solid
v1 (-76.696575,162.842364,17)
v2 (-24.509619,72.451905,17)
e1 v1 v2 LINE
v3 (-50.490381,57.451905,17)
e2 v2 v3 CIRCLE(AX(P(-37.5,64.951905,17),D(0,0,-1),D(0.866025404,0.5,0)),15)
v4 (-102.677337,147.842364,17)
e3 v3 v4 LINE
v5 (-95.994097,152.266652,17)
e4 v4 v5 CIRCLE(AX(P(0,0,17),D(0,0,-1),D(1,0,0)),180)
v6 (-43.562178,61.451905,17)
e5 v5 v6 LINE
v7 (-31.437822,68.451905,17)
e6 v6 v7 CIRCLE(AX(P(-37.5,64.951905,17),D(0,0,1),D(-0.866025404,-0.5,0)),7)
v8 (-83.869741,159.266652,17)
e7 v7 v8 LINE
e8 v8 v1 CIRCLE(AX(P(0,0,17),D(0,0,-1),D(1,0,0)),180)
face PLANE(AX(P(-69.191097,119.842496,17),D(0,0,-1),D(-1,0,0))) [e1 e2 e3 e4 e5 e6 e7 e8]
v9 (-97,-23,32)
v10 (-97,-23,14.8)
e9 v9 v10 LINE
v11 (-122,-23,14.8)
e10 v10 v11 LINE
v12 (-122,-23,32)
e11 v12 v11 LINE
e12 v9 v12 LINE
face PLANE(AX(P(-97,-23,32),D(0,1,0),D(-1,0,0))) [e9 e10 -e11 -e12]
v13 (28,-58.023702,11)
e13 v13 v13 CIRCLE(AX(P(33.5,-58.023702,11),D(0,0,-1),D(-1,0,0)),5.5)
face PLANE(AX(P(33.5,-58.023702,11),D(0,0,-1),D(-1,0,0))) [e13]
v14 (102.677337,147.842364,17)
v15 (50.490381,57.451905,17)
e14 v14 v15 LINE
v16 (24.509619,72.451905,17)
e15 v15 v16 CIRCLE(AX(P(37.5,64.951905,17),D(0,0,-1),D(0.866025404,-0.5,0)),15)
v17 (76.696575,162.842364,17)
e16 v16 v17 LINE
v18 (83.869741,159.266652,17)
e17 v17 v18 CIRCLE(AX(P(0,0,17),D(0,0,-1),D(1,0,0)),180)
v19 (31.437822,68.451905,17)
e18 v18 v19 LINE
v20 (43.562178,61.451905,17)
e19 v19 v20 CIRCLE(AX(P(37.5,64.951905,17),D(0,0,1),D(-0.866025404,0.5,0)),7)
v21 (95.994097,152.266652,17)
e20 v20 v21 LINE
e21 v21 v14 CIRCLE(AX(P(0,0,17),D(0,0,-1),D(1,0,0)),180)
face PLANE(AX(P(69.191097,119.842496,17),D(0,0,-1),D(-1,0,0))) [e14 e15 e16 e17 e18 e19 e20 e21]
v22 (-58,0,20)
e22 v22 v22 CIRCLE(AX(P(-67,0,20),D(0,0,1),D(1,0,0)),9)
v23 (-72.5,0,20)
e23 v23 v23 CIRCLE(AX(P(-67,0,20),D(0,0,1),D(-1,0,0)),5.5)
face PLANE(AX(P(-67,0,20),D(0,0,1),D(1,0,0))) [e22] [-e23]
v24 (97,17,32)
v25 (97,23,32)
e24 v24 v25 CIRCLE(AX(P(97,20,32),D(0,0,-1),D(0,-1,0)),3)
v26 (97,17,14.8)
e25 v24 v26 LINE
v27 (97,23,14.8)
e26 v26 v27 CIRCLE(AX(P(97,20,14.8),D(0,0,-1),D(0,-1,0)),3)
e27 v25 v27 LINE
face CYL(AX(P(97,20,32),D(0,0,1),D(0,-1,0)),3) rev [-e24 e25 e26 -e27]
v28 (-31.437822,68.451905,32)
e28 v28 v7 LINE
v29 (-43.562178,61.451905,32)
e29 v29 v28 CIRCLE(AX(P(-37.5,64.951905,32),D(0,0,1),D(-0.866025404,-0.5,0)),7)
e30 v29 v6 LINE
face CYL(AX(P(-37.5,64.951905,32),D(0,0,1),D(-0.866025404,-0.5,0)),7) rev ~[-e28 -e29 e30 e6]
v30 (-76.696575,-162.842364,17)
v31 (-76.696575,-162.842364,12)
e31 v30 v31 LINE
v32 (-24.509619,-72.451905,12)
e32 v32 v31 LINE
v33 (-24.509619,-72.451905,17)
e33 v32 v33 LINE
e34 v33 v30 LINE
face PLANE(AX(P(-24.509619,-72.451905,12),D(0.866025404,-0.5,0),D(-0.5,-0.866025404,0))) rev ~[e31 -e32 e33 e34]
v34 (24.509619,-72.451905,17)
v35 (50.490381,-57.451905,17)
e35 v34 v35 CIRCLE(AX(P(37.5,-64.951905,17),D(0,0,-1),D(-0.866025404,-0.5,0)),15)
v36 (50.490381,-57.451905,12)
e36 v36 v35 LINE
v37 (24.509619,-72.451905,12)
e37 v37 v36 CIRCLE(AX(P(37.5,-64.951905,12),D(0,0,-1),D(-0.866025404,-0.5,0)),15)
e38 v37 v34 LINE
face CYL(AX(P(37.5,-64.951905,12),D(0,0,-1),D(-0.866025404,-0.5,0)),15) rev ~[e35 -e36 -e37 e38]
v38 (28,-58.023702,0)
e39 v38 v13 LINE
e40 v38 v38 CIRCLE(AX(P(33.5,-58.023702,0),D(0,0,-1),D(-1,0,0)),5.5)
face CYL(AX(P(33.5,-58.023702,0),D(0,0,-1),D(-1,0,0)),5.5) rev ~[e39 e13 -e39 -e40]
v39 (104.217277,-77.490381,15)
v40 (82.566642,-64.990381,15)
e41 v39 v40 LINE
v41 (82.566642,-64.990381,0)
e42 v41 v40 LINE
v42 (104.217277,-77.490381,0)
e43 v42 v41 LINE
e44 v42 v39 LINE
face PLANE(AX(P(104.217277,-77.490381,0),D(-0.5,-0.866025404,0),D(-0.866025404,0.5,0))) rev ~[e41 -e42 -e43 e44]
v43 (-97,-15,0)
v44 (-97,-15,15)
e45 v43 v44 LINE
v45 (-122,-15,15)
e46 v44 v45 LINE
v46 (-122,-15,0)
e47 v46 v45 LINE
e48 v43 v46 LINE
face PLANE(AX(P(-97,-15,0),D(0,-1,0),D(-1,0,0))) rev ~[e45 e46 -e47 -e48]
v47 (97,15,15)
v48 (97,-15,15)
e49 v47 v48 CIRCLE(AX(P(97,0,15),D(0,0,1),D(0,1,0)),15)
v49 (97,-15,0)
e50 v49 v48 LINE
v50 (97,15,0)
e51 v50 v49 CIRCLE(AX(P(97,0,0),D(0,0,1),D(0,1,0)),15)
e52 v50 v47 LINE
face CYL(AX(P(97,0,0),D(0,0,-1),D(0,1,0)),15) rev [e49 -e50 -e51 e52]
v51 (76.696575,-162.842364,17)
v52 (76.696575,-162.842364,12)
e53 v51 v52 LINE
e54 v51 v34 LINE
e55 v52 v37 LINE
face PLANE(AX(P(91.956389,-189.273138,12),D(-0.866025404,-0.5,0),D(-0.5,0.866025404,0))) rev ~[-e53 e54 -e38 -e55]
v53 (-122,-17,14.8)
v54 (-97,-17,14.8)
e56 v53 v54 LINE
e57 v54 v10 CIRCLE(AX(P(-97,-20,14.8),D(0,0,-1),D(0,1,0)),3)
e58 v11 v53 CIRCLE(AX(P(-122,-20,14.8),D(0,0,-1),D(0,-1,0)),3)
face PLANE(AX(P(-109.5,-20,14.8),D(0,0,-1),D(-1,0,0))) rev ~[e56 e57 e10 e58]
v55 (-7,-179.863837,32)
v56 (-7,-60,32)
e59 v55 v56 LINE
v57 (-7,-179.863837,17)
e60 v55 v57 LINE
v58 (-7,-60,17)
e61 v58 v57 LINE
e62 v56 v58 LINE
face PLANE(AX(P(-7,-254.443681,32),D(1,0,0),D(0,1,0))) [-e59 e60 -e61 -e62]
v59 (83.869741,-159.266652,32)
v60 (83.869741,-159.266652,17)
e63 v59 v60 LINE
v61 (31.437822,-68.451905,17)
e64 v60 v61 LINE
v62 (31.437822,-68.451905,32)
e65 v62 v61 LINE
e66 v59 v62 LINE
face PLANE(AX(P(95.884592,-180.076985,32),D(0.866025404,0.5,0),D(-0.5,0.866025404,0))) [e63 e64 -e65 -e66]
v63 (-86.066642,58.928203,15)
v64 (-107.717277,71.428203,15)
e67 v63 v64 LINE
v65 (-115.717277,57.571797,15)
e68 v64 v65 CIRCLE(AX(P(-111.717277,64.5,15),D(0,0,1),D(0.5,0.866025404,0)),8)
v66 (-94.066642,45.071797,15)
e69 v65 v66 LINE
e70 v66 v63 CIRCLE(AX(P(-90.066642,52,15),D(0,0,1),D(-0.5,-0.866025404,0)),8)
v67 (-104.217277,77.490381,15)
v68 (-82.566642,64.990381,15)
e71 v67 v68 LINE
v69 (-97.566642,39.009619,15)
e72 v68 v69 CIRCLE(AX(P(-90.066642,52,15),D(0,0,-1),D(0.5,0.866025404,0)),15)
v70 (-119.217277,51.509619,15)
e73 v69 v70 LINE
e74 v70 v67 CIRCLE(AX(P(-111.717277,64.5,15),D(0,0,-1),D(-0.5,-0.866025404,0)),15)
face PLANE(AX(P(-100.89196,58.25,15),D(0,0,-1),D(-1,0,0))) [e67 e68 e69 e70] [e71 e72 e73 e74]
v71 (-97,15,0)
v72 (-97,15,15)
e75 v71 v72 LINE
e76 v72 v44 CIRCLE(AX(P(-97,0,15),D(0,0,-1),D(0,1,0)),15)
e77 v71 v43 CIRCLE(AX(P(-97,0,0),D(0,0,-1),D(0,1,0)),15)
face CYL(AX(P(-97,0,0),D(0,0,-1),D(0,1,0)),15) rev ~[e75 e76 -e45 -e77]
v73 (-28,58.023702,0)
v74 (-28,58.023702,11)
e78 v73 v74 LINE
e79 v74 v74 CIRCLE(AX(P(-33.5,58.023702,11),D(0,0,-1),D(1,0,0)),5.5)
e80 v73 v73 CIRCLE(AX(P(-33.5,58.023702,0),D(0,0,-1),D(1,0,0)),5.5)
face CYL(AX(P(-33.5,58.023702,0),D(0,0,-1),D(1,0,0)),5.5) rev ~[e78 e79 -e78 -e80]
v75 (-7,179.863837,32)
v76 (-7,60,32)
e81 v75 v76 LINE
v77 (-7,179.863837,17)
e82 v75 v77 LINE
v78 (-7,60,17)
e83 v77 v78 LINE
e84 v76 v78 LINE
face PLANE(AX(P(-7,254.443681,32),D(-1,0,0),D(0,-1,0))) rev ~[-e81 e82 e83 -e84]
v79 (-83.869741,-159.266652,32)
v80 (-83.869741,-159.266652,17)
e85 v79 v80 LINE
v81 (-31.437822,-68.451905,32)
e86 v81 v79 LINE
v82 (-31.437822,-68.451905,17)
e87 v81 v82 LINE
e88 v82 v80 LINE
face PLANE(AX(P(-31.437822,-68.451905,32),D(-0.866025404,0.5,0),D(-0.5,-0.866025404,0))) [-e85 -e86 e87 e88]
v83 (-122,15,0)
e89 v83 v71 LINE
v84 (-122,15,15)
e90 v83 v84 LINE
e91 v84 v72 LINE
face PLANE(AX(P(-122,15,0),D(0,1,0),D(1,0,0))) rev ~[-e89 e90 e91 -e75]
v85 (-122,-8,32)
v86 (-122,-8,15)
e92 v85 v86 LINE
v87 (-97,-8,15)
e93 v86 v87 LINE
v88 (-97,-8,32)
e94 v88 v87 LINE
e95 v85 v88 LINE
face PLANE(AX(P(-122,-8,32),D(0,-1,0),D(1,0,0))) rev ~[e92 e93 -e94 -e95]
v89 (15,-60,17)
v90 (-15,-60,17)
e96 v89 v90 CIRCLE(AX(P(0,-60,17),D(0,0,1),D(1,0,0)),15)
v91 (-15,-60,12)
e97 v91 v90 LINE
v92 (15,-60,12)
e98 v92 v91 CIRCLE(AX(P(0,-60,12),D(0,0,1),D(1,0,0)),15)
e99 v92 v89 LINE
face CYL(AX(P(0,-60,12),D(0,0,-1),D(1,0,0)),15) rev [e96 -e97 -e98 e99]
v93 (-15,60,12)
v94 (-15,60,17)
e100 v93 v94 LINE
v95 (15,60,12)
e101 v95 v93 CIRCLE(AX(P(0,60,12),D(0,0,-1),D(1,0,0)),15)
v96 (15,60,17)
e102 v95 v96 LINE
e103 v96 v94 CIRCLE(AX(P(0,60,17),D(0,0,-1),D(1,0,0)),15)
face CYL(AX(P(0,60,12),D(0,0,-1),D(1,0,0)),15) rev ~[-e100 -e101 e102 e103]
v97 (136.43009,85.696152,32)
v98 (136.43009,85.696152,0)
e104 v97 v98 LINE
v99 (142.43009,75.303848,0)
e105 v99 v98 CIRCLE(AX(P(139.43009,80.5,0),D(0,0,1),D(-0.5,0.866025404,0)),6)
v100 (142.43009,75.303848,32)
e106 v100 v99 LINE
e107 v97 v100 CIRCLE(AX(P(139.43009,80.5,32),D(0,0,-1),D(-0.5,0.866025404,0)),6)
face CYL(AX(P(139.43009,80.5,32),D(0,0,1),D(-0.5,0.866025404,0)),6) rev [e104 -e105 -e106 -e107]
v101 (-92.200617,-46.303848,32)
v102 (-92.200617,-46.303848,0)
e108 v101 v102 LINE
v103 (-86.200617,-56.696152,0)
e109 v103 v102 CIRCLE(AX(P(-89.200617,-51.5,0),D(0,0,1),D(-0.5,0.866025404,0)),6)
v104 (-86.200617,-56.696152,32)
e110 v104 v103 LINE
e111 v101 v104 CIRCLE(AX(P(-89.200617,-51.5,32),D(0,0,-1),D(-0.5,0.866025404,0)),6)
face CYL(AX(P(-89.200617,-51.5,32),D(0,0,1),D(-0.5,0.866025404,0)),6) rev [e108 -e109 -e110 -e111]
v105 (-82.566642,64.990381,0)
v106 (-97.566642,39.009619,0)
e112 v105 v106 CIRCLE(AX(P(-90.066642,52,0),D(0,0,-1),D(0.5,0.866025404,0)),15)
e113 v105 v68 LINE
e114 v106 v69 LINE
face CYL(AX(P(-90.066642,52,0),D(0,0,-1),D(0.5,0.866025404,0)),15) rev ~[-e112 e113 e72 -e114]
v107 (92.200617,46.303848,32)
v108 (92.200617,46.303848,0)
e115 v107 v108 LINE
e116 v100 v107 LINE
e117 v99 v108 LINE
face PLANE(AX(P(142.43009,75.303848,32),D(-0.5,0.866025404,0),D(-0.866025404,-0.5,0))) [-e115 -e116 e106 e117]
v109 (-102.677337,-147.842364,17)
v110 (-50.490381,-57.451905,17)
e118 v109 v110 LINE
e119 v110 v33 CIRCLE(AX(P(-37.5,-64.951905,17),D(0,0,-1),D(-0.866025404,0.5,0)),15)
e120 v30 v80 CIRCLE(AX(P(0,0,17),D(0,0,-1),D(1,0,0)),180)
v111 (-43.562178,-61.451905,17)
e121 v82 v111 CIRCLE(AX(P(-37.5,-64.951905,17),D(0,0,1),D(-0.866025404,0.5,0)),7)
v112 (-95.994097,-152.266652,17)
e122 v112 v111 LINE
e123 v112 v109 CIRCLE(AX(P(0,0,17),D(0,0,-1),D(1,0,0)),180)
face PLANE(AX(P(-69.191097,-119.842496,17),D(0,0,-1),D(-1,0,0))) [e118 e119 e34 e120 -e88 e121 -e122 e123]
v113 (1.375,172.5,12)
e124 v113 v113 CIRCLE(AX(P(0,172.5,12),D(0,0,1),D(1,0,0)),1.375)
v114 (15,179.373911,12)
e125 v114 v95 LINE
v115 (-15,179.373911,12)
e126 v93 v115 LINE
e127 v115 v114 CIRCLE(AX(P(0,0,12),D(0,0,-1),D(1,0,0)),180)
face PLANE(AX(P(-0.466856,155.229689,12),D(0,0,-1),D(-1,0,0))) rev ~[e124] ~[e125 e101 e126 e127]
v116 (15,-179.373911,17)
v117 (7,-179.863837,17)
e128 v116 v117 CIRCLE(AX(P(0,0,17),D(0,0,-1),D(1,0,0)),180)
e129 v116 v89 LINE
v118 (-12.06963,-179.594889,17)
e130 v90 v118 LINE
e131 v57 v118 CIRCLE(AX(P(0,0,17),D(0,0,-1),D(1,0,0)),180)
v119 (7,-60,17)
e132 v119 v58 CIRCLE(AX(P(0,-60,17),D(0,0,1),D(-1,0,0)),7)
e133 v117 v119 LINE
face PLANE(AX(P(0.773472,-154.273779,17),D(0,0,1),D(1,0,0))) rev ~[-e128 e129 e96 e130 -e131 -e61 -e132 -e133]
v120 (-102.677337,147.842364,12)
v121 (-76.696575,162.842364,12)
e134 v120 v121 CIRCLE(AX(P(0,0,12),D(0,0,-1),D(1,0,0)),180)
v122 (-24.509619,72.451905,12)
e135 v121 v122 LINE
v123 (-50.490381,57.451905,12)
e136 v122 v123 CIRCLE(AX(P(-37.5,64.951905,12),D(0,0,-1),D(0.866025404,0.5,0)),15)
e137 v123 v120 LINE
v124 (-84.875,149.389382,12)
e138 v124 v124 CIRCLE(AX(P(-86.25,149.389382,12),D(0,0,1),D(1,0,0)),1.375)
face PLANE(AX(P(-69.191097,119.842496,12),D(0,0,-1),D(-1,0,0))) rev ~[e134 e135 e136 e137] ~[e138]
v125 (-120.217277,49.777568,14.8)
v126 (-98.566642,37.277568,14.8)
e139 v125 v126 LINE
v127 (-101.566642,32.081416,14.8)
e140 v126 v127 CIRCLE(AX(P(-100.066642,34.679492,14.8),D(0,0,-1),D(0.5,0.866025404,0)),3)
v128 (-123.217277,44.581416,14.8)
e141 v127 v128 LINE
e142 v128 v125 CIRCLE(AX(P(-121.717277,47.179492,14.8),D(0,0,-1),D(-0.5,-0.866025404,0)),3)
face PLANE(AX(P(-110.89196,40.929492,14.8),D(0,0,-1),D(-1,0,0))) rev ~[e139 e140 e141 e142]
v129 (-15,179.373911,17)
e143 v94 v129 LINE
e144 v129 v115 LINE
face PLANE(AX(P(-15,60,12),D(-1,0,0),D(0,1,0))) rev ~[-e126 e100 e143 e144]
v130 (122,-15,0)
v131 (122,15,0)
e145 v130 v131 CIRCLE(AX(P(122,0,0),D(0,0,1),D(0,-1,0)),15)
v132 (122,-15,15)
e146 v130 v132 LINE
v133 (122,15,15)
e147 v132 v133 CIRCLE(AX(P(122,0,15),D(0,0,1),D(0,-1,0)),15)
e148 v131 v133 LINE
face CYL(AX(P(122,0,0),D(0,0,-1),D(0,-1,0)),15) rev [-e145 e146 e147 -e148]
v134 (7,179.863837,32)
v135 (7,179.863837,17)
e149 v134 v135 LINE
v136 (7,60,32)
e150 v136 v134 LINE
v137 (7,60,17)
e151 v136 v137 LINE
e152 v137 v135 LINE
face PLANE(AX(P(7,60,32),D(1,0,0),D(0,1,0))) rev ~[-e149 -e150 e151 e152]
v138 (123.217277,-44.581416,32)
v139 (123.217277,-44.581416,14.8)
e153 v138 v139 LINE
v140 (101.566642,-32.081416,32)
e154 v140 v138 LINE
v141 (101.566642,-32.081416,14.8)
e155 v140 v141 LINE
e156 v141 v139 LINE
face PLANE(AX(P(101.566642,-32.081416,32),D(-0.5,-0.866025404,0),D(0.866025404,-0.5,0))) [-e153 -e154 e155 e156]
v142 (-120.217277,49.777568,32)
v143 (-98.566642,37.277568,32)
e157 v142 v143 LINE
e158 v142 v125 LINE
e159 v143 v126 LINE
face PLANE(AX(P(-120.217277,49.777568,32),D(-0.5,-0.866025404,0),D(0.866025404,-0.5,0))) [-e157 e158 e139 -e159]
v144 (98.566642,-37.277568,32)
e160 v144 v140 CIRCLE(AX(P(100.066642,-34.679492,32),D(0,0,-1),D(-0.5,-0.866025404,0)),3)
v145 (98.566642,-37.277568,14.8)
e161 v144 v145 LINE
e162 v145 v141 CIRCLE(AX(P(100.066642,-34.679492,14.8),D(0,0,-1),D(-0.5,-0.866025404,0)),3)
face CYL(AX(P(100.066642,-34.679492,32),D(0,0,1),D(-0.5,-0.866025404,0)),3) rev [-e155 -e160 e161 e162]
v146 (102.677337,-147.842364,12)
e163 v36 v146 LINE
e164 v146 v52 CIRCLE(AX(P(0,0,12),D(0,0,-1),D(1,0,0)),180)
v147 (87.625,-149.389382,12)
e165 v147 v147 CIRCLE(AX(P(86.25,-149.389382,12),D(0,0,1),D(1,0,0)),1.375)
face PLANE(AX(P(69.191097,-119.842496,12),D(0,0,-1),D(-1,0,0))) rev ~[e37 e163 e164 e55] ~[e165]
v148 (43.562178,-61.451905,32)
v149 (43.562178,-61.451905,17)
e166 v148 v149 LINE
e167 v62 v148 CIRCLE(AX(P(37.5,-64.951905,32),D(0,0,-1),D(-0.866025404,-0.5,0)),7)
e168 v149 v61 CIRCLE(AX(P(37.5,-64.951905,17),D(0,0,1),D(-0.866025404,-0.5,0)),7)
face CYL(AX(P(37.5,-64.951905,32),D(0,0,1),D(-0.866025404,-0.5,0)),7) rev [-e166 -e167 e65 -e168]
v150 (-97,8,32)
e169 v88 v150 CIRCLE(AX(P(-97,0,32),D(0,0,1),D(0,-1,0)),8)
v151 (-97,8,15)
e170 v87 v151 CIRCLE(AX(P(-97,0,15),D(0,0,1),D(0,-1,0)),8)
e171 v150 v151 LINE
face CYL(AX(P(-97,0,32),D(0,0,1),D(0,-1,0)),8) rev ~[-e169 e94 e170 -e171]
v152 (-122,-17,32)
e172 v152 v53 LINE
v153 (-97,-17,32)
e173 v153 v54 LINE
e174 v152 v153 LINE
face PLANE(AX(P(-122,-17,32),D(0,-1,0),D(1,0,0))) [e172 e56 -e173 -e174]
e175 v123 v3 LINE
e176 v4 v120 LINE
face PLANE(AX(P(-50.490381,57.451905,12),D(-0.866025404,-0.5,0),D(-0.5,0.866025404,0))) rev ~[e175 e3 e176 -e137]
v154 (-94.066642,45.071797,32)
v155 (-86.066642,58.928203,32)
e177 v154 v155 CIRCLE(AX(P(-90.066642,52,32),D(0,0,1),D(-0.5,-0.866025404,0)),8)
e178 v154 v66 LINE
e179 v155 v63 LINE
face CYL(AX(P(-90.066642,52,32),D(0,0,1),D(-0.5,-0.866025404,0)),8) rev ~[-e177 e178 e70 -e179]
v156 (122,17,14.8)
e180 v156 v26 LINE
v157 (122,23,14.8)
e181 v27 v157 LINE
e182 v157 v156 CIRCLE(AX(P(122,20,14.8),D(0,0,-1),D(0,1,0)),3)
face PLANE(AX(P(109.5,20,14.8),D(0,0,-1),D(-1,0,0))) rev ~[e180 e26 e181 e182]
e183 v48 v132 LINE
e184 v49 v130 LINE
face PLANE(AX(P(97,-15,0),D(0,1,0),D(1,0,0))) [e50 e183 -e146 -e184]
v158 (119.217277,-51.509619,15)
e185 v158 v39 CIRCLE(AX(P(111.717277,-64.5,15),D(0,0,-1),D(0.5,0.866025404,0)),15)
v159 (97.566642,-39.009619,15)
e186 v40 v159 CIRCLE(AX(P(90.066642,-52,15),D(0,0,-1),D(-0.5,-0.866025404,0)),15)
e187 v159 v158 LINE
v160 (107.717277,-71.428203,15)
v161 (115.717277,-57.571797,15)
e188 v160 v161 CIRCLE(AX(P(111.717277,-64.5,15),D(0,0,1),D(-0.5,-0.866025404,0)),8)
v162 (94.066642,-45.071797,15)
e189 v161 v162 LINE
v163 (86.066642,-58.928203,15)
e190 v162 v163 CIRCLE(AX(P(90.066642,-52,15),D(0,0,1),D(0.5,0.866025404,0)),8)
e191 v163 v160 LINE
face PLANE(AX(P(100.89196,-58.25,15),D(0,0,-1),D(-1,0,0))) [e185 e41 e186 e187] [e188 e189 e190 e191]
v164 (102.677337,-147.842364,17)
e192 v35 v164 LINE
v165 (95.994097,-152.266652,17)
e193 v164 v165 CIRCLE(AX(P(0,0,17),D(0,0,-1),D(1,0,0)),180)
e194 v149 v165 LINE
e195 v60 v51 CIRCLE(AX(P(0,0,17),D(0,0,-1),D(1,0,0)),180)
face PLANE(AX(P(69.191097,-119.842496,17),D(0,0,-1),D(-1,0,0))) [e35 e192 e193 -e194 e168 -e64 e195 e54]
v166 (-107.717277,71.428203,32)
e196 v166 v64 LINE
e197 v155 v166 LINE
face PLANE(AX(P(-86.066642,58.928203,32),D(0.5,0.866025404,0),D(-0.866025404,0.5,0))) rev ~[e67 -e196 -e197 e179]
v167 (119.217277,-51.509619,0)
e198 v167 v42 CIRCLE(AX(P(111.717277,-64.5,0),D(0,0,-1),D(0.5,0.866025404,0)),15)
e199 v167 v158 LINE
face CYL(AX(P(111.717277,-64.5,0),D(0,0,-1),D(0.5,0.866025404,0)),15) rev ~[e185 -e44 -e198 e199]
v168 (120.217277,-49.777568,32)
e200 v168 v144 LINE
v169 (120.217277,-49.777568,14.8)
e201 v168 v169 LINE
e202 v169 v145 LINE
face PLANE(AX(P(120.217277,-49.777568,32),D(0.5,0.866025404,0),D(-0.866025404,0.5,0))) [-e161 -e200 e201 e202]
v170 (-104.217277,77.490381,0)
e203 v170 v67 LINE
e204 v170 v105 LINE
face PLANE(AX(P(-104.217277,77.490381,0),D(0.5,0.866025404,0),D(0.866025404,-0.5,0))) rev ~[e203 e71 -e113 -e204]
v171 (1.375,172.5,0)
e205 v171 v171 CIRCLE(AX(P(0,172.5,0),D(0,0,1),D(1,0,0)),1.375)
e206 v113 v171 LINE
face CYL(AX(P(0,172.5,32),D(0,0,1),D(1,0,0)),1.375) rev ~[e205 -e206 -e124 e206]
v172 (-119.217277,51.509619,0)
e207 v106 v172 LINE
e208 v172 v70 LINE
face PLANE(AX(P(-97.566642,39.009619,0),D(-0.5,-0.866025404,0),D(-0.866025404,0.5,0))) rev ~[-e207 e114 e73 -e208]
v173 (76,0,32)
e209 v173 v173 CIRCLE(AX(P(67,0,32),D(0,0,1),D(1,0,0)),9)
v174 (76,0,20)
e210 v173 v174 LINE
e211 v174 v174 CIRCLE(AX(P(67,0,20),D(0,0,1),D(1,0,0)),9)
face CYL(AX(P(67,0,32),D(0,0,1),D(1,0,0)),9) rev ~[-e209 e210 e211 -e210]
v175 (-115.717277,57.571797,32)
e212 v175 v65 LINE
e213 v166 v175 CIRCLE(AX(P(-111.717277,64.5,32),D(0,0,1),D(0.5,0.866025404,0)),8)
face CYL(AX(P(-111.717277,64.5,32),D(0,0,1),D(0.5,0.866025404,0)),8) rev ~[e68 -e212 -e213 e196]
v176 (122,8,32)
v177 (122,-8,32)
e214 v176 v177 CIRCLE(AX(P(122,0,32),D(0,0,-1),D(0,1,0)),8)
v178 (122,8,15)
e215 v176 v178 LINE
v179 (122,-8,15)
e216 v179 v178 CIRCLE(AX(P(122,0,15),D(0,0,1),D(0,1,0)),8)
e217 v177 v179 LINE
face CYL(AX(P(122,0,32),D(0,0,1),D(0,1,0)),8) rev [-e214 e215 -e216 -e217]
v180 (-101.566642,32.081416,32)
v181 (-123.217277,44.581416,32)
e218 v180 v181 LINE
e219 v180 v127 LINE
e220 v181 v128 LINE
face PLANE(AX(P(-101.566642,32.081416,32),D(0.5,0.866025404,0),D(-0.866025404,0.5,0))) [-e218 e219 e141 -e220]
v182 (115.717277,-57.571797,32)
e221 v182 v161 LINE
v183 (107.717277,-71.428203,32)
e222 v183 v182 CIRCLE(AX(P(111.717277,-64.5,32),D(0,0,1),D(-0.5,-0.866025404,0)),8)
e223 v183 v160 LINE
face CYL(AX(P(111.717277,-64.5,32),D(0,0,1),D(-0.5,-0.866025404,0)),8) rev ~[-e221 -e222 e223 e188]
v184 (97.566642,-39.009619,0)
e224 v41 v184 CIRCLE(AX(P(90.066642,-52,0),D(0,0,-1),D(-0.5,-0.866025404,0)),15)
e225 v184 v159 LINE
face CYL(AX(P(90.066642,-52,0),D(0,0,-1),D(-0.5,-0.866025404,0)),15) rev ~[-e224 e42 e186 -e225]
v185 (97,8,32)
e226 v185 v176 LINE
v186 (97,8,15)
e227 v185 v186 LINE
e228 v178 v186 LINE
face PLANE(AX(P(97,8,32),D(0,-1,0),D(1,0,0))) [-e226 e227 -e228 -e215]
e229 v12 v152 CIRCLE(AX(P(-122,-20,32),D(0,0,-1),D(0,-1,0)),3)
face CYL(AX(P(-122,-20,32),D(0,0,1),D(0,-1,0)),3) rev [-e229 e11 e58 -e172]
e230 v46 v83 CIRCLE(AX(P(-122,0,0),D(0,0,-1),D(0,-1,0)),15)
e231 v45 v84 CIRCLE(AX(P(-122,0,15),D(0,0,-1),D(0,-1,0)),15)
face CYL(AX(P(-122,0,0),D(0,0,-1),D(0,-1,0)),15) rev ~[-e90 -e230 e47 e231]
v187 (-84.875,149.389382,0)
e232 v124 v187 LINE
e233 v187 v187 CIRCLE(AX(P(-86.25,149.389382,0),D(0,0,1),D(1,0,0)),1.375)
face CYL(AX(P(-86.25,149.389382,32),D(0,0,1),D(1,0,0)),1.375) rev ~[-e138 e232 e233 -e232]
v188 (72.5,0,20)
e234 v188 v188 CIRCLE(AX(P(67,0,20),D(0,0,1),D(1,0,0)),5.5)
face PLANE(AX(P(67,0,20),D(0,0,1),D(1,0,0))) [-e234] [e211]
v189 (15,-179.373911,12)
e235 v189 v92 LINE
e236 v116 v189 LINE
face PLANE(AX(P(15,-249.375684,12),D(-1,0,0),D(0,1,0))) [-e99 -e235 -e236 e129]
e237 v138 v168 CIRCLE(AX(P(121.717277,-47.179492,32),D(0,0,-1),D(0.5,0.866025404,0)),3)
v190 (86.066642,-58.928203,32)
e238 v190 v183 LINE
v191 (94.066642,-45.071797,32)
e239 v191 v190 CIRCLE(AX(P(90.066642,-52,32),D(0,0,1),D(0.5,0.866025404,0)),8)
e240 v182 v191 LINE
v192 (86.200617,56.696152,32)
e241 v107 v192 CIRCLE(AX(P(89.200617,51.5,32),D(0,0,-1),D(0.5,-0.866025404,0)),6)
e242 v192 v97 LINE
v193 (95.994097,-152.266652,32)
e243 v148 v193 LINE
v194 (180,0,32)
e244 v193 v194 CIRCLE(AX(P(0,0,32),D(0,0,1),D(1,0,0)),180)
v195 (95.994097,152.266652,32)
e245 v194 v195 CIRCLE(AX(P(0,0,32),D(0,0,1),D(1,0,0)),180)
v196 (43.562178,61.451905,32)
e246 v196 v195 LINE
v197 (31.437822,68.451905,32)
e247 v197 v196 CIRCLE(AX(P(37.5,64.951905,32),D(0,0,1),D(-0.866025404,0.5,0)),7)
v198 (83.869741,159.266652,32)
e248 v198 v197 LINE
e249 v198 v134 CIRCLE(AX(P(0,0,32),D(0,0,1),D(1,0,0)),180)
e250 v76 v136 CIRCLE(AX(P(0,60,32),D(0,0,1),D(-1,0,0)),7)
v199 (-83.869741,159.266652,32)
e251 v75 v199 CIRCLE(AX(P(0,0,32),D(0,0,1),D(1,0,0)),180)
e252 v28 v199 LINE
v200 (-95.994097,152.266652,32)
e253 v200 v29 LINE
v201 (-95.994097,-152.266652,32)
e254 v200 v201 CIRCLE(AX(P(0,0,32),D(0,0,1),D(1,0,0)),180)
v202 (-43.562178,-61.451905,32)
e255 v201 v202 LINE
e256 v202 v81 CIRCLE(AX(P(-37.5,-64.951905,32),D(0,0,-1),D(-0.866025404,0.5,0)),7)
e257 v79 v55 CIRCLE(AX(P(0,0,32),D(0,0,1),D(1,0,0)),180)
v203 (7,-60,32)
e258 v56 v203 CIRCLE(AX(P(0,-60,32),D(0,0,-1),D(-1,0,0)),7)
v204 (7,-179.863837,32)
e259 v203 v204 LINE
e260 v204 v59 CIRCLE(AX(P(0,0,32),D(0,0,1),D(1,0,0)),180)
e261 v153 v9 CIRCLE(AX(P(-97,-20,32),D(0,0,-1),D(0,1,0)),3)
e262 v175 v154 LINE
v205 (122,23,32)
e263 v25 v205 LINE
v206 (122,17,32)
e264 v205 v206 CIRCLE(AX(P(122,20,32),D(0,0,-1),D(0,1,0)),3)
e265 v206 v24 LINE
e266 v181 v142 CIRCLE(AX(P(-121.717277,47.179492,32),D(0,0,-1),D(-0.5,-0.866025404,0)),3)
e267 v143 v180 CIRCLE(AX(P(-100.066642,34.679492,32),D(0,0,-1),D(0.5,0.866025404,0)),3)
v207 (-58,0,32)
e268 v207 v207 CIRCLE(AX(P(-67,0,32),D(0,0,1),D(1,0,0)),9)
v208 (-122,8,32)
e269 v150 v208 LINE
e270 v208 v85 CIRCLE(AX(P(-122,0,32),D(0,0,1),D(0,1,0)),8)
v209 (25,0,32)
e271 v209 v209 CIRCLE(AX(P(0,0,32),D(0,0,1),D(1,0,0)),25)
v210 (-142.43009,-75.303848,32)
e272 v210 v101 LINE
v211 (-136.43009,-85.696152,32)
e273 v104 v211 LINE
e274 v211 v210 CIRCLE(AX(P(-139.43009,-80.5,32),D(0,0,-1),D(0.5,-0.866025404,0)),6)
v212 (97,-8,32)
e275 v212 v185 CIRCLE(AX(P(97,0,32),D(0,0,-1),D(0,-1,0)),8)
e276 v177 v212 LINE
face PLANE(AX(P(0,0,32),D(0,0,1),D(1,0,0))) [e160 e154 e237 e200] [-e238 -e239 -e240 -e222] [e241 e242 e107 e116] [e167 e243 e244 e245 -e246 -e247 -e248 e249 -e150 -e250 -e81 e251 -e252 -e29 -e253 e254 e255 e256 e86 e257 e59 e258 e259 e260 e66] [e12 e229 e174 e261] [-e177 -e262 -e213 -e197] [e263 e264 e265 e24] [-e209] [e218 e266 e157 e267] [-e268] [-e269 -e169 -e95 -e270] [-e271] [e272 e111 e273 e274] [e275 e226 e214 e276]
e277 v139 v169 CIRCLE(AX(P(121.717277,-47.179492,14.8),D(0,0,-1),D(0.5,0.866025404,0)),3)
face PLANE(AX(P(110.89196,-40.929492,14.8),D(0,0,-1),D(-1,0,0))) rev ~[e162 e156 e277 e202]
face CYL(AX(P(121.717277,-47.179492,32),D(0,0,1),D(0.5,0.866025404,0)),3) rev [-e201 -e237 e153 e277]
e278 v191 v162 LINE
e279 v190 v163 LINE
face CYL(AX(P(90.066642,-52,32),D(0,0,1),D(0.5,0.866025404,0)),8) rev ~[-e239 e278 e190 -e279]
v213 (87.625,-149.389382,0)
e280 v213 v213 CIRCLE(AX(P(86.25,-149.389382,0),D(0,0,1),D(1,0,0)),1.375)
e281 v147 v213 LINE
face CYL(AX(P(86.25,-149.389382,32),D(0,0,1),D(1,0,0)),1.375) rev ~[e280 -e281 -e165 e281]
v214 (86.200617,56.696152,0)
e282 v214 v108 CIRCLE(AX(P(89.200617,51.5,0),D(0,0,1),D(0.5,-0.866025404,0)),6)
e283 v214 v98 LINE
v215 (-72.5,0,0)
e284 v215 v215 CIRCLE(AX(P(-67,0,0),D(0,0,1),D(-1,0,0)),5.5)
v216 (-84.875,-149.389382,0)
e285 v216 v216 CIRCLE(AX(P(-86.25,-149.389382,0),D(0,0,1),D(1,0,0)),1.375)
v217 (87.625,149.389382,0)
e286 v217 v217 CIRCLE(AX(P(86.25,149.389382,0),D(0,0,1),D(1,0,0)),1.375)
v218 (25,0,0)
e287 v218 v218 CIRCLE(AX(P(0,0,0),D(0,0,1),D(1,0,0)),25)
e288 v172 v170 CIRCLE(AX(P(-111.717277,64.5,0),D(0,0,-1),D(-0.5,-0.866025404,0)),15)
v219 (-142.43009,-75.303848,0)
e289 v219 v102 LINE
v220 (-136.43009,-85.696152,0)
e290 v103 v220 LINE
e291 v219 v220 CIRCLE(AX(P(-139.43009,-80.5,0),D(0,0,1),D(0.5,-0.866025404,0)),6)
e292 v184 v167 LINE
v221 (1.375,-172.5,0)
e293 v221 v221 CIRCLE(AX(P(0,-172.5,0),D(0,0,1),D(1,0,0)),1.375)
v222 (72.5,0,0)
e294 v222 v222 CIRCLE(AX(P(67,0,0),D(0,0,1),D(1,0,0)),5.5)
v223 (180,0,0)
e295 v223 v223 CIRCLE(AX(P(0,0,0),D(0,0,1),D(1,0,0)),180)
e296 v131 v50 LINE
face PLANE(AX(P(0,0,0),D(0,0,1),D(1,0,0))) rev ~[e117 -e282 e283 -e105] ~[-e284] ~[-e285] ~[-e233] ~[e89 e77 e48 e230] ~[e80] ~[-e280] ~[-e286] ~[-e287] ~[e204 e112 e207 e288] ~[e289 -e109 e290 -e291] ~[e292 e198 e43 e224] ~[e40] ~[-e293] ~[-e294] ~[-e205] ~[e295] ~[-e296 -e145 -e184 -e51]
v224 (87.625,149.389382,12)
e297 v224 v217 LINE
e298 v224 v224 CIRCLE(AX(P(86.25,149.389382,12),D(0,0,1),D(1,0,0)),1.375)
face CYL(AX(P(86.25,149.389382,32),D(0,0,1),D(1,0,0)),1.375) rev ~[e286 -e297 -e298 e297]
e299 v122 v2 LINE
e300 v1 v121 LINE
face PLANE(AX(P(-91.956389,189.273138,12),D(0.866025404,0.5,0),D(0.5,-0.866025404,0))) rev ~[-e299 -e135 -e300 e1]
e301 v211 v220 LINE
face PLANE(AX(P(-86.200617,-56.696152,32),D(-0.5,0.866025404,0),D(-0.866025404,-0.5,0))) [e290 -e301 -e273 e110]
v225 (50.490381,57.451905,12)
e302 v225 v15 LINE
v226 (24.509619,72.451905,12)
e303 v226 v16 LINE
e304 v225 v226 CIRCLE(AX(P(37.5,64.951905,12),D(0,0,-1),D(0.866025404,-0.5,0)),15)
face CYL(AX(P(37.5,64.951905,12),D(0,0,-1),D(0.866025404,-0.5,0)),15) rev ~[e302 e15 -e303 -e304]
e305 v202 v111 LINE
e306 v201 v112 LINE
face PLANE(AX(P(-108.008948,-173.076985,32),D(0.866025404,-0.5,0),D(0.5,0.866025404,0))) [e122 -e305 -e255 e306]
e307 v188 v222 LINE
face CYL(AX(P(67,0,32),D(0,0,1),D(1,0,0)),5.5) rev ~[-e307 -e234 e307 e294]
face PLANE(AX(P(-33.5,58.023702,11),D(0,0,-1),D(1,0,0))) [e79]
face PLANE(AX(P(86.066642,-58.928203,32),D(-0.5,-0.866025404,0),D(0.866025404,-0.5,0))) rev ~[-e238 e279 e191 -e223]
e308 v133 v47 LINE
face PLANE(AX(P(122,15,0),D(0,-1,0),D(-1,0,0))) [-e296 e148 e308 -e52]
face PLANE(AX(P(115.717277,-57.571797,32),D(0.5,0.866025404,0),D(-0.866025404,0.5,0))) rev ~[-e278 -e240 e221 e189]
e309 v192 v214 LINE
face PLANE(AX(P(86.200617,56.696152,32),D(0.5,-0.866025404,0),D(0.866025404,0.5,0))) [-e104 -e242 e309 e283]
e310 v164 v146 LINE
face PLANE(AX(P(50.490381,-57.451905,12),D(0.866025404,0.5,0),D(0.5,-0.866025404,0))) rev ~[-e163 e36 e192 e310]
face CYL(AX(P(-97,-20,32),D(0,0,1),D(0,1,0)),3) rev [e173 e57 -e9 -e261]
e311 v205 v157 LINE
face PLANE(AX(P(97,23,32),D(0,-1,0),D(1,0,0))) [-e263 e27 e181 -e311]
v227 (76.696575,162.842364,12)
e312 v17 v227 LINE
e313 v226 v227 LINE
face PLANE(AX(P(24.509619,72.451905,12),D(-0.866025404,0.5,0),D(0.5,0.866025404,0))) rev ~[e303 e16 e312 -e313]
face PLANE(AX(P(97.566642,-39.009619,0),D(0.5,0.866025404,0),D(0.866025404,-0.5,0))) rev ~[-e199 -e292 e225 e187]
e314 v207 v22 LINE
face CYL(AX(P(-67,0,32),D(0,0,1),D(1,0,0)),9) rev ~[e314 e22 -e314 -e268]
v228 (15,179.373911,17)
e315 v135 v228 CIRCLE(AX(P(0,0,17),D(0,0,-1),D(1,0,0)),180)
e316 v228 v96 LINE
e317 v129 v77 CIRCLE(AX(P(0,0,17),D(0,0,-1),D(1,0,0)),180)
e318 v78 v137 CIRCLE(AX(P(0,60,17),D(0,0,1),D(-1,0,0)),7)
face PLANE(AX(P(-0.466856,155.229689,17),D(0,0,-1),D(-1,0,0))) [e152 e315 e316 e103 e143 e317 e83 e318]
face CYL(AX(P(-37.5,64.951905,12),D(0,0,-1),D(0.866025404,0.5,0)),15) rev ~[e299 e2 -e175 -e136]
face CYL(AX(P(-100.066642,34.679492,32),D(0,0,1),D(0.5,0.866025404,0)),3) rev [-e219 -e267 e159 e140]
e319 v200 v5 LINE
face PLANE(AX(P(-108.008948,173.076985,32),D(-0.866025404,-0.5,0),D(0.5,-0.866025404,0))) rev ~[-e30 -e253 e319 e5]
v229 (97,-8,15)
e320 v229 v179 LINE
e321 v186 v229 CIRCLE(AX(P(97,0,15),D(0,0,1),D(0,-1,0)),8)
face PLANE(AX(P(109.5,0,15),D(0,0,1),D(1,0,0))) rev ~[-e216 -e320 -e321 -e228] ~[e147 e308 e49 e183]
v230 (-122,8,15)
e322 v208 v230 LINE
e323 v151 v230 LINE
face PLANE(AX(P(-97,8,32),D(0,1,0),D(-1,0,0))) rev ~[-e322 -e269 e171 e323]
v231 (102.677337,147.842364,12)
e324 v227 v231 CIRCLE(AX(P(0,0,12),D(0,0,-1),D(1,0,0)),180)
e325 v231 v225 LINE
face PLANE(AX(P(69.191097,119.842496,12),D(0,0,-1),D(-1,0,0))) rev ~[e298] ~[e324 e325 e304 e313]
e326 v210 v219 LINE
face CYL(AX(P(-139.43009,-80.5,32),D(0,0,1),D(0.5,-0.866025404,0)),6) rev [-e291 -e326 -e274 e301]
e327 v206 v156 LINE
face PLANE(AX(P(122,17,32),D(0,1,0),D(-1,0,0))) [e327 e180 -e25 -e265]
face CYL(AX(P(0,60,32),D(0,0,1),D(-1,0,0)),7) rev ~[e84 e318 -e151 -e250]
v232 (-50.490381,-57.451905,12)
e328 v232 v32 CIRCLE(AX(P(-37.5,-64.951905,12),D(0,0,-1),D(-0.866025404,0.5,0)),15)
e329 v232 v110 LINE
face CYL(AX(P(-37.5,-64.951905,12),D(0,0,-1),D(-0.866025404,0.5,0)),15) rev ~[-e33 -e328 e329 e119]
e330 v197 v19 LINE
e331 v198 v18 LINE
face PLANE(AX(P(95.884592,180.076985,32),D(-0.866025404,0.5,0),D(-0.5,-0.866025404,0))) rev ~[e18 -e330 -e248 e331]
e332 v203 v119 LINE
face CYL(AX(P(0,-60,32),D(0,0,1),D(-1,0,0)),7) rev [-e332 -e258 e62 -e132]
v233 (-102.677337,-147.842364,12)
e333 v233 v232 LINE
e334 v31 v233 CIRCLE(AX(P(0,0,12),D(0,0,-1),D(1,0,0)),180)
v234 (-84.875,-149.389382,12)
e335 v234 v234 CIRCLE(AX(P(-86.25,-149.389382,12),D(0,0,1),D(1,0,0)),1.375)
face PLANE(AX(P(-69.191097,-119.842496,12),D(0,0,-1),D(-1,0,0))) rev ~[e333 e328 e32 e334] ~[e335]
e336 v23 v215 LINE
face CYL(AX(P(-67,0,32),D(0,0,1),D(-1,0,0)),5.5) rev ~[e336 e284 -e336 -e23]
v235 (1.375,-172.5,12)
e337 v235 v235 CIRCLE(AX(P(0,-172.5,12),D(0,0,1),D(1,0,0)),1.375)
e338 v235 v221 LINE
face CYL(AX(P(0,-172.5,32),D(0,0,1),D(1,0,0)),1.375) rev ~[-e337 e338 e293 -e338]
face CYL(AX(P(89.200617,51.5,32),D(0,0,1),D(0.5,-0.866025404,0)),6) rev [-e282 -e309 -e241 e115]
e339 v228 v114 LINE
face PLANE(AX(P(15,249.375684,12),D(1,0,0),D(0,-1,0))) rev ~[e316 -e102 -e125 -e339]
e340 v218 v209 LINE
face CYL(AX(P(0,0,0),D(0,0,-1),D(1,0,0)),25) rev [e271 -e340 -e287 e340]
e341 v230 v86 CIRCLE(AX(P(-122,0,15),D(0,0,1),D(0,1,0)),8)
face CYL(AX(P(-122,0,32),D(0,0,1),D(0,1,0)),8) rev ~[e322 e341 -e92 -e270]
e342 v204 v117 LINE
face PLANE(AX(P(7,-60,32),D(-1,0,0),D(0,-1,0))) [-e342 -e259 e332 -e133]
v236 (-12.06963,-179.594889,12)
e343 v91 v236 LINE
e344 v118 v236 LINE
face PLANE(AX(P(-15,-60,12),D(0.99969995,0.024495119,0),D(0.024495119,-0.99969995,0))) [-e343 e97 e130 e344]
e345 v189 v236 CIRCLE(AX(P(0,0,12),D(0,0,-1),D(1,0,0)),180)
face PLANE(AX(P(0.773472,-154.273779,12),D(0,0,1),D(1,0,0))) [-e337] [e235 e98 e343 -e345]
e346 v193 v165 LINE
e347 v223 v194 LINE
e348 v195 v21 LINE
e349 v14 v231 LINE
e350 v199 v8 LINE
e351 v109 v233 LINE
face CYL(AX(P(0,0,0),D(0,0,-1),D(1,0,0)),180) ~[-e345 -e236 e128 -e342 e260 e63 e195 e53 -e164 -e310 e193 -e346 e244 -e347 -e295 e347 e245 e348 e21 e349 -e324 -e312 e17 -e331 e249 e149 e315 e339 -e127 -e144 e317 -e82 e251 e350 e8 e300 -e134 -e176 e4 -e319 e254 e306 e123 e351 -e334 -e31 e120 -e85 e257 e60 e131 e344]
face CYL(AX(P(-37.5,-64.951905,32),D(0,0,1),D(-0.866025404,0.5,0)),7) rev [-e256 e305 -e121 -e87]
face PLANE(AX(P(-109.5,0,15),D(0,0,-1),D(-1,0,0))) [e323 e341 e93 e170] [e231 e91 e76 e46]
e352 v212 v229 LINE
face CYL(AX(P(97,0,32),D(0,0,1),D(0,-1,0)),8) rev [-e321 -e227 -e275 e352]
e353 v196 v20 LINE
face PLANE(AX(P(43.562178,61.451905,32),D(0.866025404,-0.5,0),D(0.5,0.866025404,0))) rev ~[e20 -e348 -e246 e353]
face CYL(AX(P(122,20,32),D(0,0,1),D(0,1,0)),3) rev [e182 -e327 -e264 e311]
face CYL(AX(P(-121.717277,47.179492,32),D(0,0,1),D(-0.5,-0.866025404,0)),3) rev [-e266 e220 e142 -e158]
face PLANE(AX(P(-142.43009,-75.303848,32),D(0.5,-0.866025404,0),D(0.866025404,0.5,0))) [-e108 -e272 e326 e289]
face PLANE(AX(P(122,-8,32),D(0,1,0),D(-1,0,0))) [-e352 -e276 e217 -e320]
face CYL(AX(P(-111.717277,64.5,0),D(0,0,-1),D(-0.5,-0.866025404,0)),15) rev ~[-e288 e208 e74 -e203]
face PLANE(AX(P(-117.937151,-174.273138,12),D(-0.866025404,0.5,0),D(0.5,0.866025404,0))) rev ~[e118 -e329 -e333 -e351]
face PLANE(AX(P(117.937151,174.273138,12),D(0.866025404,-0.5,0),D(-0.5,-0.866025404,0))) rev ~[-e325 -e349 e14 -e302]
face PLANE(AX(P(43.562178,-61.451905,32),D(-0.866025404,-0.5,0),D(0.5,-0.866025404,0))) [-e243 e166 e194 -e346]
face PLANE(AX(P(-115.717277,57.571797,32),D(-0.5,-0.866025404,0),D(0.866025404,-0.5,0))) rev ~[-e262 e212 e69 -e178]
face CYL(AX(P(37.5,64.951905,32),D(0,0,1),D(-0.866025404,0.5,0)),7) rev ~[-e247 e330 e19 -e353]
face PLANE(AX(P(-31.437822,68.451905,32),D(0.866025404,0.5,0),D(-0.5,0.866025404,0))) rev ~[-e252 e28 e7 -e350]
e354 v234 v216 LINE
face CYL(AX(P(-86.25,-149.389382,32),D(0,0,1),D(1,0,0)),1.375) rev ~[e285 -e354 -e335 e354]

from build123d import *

# Parameters (mm, degrees)
SKETCH1_R           = 180
SKETCH1_R_2         = 25
BOSS_EXTRUDE1_DEPTH = 32
SKETCH2_R           = 5.5
CUT_EXTRUDE1_DEPTH  = 257.561883373
CUT_EXTRUDE3_DEPTH  = 257.561883373
CUT_EXTRUDE4_DEPTH  = 5
CUT_EXTRUDE5_REACH  = 258.562
SKETCH7_R           = 1.375
CUT_EXTRUDE6_DEPTH  = 257.561883373
CUT_EXTRUDE7_DEPTH  = 17.2
CUT_EXTRUDE8_START  = -32
CUT_EXTRUDE8_DEPTH  = 15
SKETCH11_R          = 9
CUT_EXTRUDE9_DEPTH  = 12
SKETCH12_R          = 5.5
CUT_EXTRUDE10_DEPTH = 11


with BuildPart() as part:
    # Sketch1 → Boss-Extrude1 (new body)
    with BuildSketch(Plane.XY):
        Circle(SKETCH1_R)
        Circle(SKETCH1_R_2, mode=Mode.SUBTRACT)
    extrude(amount=BOSS_EXTRUDE1_DEPTH)

    # Sketch2 → Cut-Extrude1 (cut, through all)
    with BuildSketch(Plane.XY.offset(32)):
        with Locations((67, 0)):
            Circle(SKETCH2_R)
        with Locations(Location((-67, 0, 0), (0, 0, 180))):
            Circle(SKETCH2_R)
    extrude(amount=-CUT_EXTRUDE1_DEPTH, mode=Mode.SUBTRACT)

    # Sketch3 → Cut-Extrude3 (cut, through all)
    with BuildSketch(Plane.XY.offset(32)):
        with BuildLine():
            Line((-86.20061659, -56.696152423), (-136.430090009, -85.696152423))
            ThreePointArc((-136.430090009, -85.696152423), (-144.626242432, -83.5), (-142.430090009, -75.303847577))
            Line((-142.430090009, -75.303847577), (-92.20061659, -46.303847577))
            ThreePointArc((-92.20061659, -46.303847577), (-84.004464167, -48.5), (-86.20061659, -56.696152423))
        make_face()
        with BuildLine():
            Line((86.20061659, 56.696152423), (136.430090009, 85.696152423))
            ThreePointArc((136.430090009, 85.696152423), (144.626242432, 83.5), (142.430090009, 75.303847577))
            Line((142.430090009, 75.303847577), (92.20061659, 46.303847577))
            ThreePointArc((92.20061659, 46.303847577), (84.004464167, 48.5), (86.20061659, 56.696152423))
        make_face()
    extrude(amount=-CUT_EXTRUDE3_DEPTH, mode=Mode.SUBTRACT)

    # Sketch5 → Cut-Extrude4 (cut)
    with BuildSketch(Plane(origin=(0, 0, 12), x_dir=(-1, 0, 0), z_dir=(0, 0, -1))):
        with BuildLine():
            Line((15, 60), (15, 264.061054266))
            Line((15, 264.061054266), (-15, 249.37568409))
            Line((-15, 249.37568409), (-15, 60))
            ThreePointArc((-15, 60), (0, 45), (15, 60))
        make_face()
        with BuildLine():
            Line((-91.956389003, 189.273137833), (-117.937151116, 174.273137833))
            Line((-117.937151116, 174.273137833), (-50.490381057, 57.451905284))
            ThreePointArc((-50.490381057, 57.451905284), (-30, 51.961524227), (-24.509618943, 72.451905284))
            Line((-24.509618943, 72.451905284), (-91.956389003, 189.273137833))
        make_face()
        with BuildLine():
            Line((91.956389003, 189.273137833), (24.509618943, 72.451905284))
            ThreePointArc((24.509618943, 72.451905284), (30, 51.961524227), (50.490381057, 57.451905284))
            Line((50.490381057, 57.451905284), (117.937151116, 174.273137833))
            Line((117.937151116, 174.273137833), (91.956389003, 189.273137833))
        make_face()
        with BuildLine():
            Line((91.956389003, -189.273137833), (117.937151116, -174.273137833))
            Line((117.937151116, -174.273137833), (50.490381057, -57.451905284))
            ThreePointArc((50.490381057, -57.451905284), (30, -51.961524227), (24.509618943, -72.451905284))
            Line((24.509618943, -72.451905284), (91.956389003, -189.273137833))
        make_face()
        with BuildLine():
            Line((-91.956389003, -189.273137833), (-24.509618943, -72.451905284))
            ThreePointArc((-24.509618943, -72.451905284), (-30, -51.961524227), (-50.490381057, -57.451905284))
            Line((-50.490381057, -57.451905284), (-117.937151116, -174.273137833))
            Line((-117.937151116, -174.273137833), (-91.956389003, -189.273137833))
        make_face()
        with BuildLine():
            Line((10, -264.061054266), (-15, -249.37568409))
            Line((-15, -249.37568409), (-15, -60))
            ThreePointArc((-15, -60), (0, -45), (15, -60))
            Line((15, -60), (10, -264.061054266))
        make_face()
    extrude(amount=-CUT_EXTRUDE4_DEPTH, mode=Mode.SUBTRACT)

    # Sketch6 → Cut-Extrude5 (cut, up to next)
    with BuildSketch(Plane.XY.offset(32), mode=Mode.PRIVATE) as cut_extrude5_sk1:
        with BuildLine():
            Line((-95.884592233, -180.076985411), (-108.008947886, -173.076985411))
            Line((-108.008947886, -173.076985411), (-43.562177826, -61.451905284))
            ThreePointArc((-43.562177826, -61.451905284), (-34, -58.889727457), (-31.437822174, -68.451905284))
            Line((-31.437822174, -68.451905284), (-95.884592233, -180.076985411))
        make_face()
    cut_extrude5_tool1 = extrude(cut_extrude5_sk1.sketch, amount=-CUT_EXTRUDE5_REACH, mode=Mode.PRIVATE) & part.part
    # Sketch6 → Cut-Extrude5 (cut, up to next)
    with BuildSketch(Plane.XY.offset(32), mode=Mode.PRIVATE) as cut_extrude5_sk2:
        with BuildLine():
            Line((-7, -254.443680545), (-7, -60))
            ThreePointArc((-7, -60), (0, -53), (7, -60))
            Line((7, -60), (7, -245.63245844))
            Line((7, -245.63245844), (-7, -254.443680545))
        make_face()
    cut_extrude5_tool2 = extrude(cut_extrude5_sk2.sketch, amount=-CUT_EXTRUDE5_REACH, mode=Mode.PRIVATE) & part.part
    # Sketch6 → Cut-Extrude5 (cut, up to next)
    with BuildSketch(Plane.XY.offset(32), mode=Mode.PRIVATE) as cut_extrude5_sk3:
        with BuildLine():
            Line((43.562177826, -61.451905284), (108.008947886, -173.076985411))
            Line((108.008947886, -173.076985411), (95.884592233, -180.076985411))
            Line((95.884592233, -180.076985411), (31.437822174, -68.451905284))
            ThreePointArc((31.437822174, -68.451905284), (34, -58.889727457), (43.562177826, -61.451905284))
        make_face()
    cut_extrude5_tool3 = extrude(cut_extrude5_sk3.sketch, amount=-CUT_EXTRUDE5_REACH, mode=Mode.PRIVATE) & part.part
    # Sketch6 → Cut-Extrude5 (cut, up to next)
    with BuildSketch(Plane.XY.offset(32), mode=Mode.PRIVATE) as cut_extrude5_sk4:
        with BuildLine():
            Line((108.008947886, 173.076985411), (95.884592233, 180.076985411))
            Line((95.884592233, 180.076985411), (31.437822174, 68.451905284))
            ThreePointArc((31.437822174, 68.451905284), (34, 58.889727457), (43.562177826, 61.451905284))
            Line((43.562177826, 61.451905284), (108.008947886, 173.076985411))
        make_face()
    cut_extrude5_tool4 = extrude(cut_extrude5_sk4.sketch, amount=-CUT_EXTRUDE5_REACH, mode=Mode.PRIVATE) & part.part
    # Sketch6 → Cut-Extrude5 (cut, up to next)
    with BuildSketch(Plane.XY.offset(32), mode=Mode.PRIVATE) as cut_extrude5_sk5:
        with BuildLine():
            Line((7, 60), (7, 245.63245844))
            Line((7, 245.63245844), (-7, 254.443680545))
            Line((-7, 254.443680545), (-7, 60))
            ThreePointArc((-7, 60), (0, 53), (7, 60))
        make_face()
    cut_extrude5_tool5 = extrude(cut_extrude5_sk5.sketch, amount=-CUT_EXTRUDE5_REACH, mode=Mode.PRIVATE) & part.part
    # Sketch6 → Cut-Extrude5 (cut, up to next)
    with BuildSketch(Plane.XY.offset(32), mode=Mode.PRIVATE) as cut_extrude5_sk6:
        with BuildLine():
            Line((-31.437822174, 68.451905284), (-95.884592233, 180.076985411))
            Line((-95.884592233, 180.076985411), (-108.008947886, 173.076985411))
            Line((-108.008947886, 173.076985411), (-43.562177826, 61.451905284))
            ThreePointArc((-43.562177826, 61.451905284), (-34, 58.889727457), (-31.437822174, 68.451905284))
        make_face()
    cut_extrude5_tool6 = extrude(cut_extrude5_sk6.sketch, amount=-CUT_EXTRUDE5_REACH, mode=Mode.PRIVATE) & part.part
    add(cut_extrude5_tool1.solids().sort_by_distance((-68.344397, -118.375969, 32))[0], mode=Mode.SUBTRACT)
    add(cut_extrude5_tool2.solids().sort_by_distance((-0.052572, -152.280443, 32))[0], mode=Mode.SUBTRACT)
    add(cut_extrude5_tool3.solids().sort_by_distance((68.344397, -118.375969, 32))[0], mode=Mode.SUBTRACT)
    add(cut_extrude5_tool4.solids().sort_by_distance((68.344397, 118.375969, 32))[0], mode=Mode.SUBTRACT)
    add(cut_extrude5_tool5.solids().sort_by_distance((-0.052572, 152.280443, 32))[0], mode=Mode.SUBTRACT)
    add(cut_extrude5_tool6.solids().sort_by_distance((-68.344397, 118.375969, 32))[0], mode=Mode.SUBTRACT)

    # Sketch7 → Cut-Extrude6 (cut, through all)
    with BuildSketch(Plane.XY.offset(32)):
        with Locations((0, 172.5)):
            Circle(SKETCH7_R)
        with Locations((86.25, 149.389382153)):
            Circle(SKETCH7_R)
        with Locations((86.25, -149.389382153)):
            Circle(SKETCH7_R)
        with Locations((0, -172.5)):
            Circle(SKETCH7_R)
        with Locations((-86.25, -149.389382153)):
            Circle(SKETCH7_R)
        with Locations((-86.25, 149.389382153)):
            Circle(SKETCH7_R)
    extrude(amount=-CUT_EXTRUDE6_DEPTH, mode=Mode.SUBTRACT)

    # Sketch8 → Cut-Extrude7 (cut)
    with BuildSketch(Plane.XY.offset(32)):
        with BuildLine():
            Line((97, 8), (122, 8))
            ThreePointArc((122, 8), (130, 0), (122, -8))
            Line((122, -8), (97, -8))
            ThreePointArc((97, -8), (89, 0), (97, 8))
        make_face()
        with BuildLine():
            Line((97, 23), (122, 23))
            ThreePointArc((122, 23), (125, 20), (122, 17))
            Line((122, 17), (97, 17))
            ThreePointArc((97, 17), (94, 20), (97, 23))
        make_face()
        with BuildLine():
            Line((120.217277088, -49.777568136), (98.566641994, -37.277568136))
            ThreePointArc((98.566641994, -37.277568136), (97.468565782, -33.179491924), (101.566641994, -32.081415713))
            Line((101.566641994, -32.081415713), (123.217277088, -44.581415713))
            ThreePointArc((123.217277088, -44.581415713), (124.3153533, -48.679491924), (120.217277088, -49.777568136))
        make_face()
        with BuildLine():
            Line((-97, 8), (-122, 8))
            ThreePointArc((-122, 8), (-130, 0), (-122, -8))
            Line((-122, -8), (-97, -8))
            ThreePointArc((-97, -8), (-89, 0), (-97, 8))
        make_face()
        with BuildLine():
            Line((-122, -17), (-97, -17))
            ThreePointArc((-97, -17), (-94, -20), (-97, -23))
            Line((-97, -23), (-122, -23))
            ThreePointArc((-122, -23), (-125, -20), (-122, -17))
        make_face()
        with BuildLine():
            Line((86.066641994, -58.92820323), (107.717277088, -71.42820323))
            ThreePointArc((107.717277088, -71.42820323), (118.645480318, -68.5), (115.717277088, -57.57179677))
            Line((115.717277088, -57.57179677), (94.066641994, -45.07179677))
            ThreePointArc((94.066641994, -45.07179677), (83.138438763, -48), (86.066641994, -58.92820323))
        make_face()
        with BuildLine():
            Line((-86.066641994, 58.92820323), (-107.717277088, 71.42820323))
            ThreePointArc((-107.717277088, 71.42820323), (-118.645480318, 68.5), (-115.717277088, 57.57179677))
            Line((-115.717277088, 57.57179677), (-94.066641994, 45.07179677))
            ThreePointArc((-94.066641994, 45.07179677), (-83.138438763, 48), (-86.066641994, 58.92820323))
        make_face()
        with BuildLine():
            Line((-120.217277088, 49.777568136), (-98.566641994, 37.277568136))
            ThreePointArc((-98.566641994, 37.277568136), (-97.468565782, 33.179491924), (-101.566641994, 32.081415713))
            Line((-101.566641994, 32.081415713), (-123.217277088, 44.581415713))
            ThreePointArc((-123.217277088, 44.581415713), (-124.3153533, 48.679491924), (-120.217277088, 49.777568136))
        make_face()
    extrude(amount=-CUT_EXTRUDE7_DEPTH, mode=Mode.SUBTRACT)

    # Sketch9 → Cut-Extrude8 (cut)
    with BuildSketch(Plane.XY.offset(32).offset(CUT_EXTRUDE8_START)):
        with BuildLine():
            Line((-104.217277088, 77.490381057), (-82.566641994, 64.990381057))
            ThreePointArc((-82.566641994, 64.990381057), (-77.076260937, 44.5), (-97.566641994, 39.009618943))
            Line((-97.566641994, 39.009618943), (-119.217277088, 51.509618943))
            ThreePointArc((-119.217277088, 51.509618943), (-124.707658145, 72), (-104.217277088, 77.490381057))
        make_face()
        with BuildLine():
            Line((-122, 15), (-97, 15))
            ThreePointArc((-97, 15), (-82, 0), (-97, -15))
            Line((-97, -15), (-122, -15))
            ThreePointArc((-122, -15), (-137, 0), (-122, 15))
        make_face()
        with BuildLine():
            Line((97, -15), (122, -15))
            ThreePointArc((122, -15), (137, 0), (122, 15))
            Line((122, 15), (97, 15))
            ThreePointArc((97, 15), (82, 0), (97, -15))
        make_face()
        with BuildLine():
            Line((104.217277088, -77.490381057), (82.566641994, -64.990381057))
            ThreePointArc((82.566641994, -64.990381057), (77.076260937, -44.5), (97.566641994, -39.009618943))
            Line((97.566641994, -39.009618943), (119.217277088, -51.509618943))
            ThreePointArc((119.217277088, -51.509618943), (124.707658145, -72), (104.217277088, -77.490381057))
        make_face()
    extrude(amount=CUT_EXTRUDE8_DEPTH, mode=Mode.SUBTRACT)

    # Sketch11 → Cut-Extrude9 (cut)
    with BuildSketch(Plane.XY.offset(32)):
        with Locations((-67, 0)):
            Circle(SKETCH11_R)
        with Locations((67, 0)):
            Circle(SKETCH11_R)
    extrude(amount=-CUT_EXTRUDE9_DEPTH, mode=Mode.SUBTRACT)

    # Sketch12 → Cut-Extrude10 (cut)
    with BuildSketch(Plane(origin=(0, 0, 0), x_dir=(-1, 0, 0), z_dir=(0, 0, -1))):
        with Locations((-33.5, -58.023702054)):
            Circle(SKETCH12_R)
        with Locations(Location((33.5, 58.023702054, 0), (0, 0, 180))):
            Circle(SKETCH12_R)
    extrude(amount=-CUT_EXTRUDE10_DEPTH, mode=Mode.SUBTRACT)


solid = part.part
